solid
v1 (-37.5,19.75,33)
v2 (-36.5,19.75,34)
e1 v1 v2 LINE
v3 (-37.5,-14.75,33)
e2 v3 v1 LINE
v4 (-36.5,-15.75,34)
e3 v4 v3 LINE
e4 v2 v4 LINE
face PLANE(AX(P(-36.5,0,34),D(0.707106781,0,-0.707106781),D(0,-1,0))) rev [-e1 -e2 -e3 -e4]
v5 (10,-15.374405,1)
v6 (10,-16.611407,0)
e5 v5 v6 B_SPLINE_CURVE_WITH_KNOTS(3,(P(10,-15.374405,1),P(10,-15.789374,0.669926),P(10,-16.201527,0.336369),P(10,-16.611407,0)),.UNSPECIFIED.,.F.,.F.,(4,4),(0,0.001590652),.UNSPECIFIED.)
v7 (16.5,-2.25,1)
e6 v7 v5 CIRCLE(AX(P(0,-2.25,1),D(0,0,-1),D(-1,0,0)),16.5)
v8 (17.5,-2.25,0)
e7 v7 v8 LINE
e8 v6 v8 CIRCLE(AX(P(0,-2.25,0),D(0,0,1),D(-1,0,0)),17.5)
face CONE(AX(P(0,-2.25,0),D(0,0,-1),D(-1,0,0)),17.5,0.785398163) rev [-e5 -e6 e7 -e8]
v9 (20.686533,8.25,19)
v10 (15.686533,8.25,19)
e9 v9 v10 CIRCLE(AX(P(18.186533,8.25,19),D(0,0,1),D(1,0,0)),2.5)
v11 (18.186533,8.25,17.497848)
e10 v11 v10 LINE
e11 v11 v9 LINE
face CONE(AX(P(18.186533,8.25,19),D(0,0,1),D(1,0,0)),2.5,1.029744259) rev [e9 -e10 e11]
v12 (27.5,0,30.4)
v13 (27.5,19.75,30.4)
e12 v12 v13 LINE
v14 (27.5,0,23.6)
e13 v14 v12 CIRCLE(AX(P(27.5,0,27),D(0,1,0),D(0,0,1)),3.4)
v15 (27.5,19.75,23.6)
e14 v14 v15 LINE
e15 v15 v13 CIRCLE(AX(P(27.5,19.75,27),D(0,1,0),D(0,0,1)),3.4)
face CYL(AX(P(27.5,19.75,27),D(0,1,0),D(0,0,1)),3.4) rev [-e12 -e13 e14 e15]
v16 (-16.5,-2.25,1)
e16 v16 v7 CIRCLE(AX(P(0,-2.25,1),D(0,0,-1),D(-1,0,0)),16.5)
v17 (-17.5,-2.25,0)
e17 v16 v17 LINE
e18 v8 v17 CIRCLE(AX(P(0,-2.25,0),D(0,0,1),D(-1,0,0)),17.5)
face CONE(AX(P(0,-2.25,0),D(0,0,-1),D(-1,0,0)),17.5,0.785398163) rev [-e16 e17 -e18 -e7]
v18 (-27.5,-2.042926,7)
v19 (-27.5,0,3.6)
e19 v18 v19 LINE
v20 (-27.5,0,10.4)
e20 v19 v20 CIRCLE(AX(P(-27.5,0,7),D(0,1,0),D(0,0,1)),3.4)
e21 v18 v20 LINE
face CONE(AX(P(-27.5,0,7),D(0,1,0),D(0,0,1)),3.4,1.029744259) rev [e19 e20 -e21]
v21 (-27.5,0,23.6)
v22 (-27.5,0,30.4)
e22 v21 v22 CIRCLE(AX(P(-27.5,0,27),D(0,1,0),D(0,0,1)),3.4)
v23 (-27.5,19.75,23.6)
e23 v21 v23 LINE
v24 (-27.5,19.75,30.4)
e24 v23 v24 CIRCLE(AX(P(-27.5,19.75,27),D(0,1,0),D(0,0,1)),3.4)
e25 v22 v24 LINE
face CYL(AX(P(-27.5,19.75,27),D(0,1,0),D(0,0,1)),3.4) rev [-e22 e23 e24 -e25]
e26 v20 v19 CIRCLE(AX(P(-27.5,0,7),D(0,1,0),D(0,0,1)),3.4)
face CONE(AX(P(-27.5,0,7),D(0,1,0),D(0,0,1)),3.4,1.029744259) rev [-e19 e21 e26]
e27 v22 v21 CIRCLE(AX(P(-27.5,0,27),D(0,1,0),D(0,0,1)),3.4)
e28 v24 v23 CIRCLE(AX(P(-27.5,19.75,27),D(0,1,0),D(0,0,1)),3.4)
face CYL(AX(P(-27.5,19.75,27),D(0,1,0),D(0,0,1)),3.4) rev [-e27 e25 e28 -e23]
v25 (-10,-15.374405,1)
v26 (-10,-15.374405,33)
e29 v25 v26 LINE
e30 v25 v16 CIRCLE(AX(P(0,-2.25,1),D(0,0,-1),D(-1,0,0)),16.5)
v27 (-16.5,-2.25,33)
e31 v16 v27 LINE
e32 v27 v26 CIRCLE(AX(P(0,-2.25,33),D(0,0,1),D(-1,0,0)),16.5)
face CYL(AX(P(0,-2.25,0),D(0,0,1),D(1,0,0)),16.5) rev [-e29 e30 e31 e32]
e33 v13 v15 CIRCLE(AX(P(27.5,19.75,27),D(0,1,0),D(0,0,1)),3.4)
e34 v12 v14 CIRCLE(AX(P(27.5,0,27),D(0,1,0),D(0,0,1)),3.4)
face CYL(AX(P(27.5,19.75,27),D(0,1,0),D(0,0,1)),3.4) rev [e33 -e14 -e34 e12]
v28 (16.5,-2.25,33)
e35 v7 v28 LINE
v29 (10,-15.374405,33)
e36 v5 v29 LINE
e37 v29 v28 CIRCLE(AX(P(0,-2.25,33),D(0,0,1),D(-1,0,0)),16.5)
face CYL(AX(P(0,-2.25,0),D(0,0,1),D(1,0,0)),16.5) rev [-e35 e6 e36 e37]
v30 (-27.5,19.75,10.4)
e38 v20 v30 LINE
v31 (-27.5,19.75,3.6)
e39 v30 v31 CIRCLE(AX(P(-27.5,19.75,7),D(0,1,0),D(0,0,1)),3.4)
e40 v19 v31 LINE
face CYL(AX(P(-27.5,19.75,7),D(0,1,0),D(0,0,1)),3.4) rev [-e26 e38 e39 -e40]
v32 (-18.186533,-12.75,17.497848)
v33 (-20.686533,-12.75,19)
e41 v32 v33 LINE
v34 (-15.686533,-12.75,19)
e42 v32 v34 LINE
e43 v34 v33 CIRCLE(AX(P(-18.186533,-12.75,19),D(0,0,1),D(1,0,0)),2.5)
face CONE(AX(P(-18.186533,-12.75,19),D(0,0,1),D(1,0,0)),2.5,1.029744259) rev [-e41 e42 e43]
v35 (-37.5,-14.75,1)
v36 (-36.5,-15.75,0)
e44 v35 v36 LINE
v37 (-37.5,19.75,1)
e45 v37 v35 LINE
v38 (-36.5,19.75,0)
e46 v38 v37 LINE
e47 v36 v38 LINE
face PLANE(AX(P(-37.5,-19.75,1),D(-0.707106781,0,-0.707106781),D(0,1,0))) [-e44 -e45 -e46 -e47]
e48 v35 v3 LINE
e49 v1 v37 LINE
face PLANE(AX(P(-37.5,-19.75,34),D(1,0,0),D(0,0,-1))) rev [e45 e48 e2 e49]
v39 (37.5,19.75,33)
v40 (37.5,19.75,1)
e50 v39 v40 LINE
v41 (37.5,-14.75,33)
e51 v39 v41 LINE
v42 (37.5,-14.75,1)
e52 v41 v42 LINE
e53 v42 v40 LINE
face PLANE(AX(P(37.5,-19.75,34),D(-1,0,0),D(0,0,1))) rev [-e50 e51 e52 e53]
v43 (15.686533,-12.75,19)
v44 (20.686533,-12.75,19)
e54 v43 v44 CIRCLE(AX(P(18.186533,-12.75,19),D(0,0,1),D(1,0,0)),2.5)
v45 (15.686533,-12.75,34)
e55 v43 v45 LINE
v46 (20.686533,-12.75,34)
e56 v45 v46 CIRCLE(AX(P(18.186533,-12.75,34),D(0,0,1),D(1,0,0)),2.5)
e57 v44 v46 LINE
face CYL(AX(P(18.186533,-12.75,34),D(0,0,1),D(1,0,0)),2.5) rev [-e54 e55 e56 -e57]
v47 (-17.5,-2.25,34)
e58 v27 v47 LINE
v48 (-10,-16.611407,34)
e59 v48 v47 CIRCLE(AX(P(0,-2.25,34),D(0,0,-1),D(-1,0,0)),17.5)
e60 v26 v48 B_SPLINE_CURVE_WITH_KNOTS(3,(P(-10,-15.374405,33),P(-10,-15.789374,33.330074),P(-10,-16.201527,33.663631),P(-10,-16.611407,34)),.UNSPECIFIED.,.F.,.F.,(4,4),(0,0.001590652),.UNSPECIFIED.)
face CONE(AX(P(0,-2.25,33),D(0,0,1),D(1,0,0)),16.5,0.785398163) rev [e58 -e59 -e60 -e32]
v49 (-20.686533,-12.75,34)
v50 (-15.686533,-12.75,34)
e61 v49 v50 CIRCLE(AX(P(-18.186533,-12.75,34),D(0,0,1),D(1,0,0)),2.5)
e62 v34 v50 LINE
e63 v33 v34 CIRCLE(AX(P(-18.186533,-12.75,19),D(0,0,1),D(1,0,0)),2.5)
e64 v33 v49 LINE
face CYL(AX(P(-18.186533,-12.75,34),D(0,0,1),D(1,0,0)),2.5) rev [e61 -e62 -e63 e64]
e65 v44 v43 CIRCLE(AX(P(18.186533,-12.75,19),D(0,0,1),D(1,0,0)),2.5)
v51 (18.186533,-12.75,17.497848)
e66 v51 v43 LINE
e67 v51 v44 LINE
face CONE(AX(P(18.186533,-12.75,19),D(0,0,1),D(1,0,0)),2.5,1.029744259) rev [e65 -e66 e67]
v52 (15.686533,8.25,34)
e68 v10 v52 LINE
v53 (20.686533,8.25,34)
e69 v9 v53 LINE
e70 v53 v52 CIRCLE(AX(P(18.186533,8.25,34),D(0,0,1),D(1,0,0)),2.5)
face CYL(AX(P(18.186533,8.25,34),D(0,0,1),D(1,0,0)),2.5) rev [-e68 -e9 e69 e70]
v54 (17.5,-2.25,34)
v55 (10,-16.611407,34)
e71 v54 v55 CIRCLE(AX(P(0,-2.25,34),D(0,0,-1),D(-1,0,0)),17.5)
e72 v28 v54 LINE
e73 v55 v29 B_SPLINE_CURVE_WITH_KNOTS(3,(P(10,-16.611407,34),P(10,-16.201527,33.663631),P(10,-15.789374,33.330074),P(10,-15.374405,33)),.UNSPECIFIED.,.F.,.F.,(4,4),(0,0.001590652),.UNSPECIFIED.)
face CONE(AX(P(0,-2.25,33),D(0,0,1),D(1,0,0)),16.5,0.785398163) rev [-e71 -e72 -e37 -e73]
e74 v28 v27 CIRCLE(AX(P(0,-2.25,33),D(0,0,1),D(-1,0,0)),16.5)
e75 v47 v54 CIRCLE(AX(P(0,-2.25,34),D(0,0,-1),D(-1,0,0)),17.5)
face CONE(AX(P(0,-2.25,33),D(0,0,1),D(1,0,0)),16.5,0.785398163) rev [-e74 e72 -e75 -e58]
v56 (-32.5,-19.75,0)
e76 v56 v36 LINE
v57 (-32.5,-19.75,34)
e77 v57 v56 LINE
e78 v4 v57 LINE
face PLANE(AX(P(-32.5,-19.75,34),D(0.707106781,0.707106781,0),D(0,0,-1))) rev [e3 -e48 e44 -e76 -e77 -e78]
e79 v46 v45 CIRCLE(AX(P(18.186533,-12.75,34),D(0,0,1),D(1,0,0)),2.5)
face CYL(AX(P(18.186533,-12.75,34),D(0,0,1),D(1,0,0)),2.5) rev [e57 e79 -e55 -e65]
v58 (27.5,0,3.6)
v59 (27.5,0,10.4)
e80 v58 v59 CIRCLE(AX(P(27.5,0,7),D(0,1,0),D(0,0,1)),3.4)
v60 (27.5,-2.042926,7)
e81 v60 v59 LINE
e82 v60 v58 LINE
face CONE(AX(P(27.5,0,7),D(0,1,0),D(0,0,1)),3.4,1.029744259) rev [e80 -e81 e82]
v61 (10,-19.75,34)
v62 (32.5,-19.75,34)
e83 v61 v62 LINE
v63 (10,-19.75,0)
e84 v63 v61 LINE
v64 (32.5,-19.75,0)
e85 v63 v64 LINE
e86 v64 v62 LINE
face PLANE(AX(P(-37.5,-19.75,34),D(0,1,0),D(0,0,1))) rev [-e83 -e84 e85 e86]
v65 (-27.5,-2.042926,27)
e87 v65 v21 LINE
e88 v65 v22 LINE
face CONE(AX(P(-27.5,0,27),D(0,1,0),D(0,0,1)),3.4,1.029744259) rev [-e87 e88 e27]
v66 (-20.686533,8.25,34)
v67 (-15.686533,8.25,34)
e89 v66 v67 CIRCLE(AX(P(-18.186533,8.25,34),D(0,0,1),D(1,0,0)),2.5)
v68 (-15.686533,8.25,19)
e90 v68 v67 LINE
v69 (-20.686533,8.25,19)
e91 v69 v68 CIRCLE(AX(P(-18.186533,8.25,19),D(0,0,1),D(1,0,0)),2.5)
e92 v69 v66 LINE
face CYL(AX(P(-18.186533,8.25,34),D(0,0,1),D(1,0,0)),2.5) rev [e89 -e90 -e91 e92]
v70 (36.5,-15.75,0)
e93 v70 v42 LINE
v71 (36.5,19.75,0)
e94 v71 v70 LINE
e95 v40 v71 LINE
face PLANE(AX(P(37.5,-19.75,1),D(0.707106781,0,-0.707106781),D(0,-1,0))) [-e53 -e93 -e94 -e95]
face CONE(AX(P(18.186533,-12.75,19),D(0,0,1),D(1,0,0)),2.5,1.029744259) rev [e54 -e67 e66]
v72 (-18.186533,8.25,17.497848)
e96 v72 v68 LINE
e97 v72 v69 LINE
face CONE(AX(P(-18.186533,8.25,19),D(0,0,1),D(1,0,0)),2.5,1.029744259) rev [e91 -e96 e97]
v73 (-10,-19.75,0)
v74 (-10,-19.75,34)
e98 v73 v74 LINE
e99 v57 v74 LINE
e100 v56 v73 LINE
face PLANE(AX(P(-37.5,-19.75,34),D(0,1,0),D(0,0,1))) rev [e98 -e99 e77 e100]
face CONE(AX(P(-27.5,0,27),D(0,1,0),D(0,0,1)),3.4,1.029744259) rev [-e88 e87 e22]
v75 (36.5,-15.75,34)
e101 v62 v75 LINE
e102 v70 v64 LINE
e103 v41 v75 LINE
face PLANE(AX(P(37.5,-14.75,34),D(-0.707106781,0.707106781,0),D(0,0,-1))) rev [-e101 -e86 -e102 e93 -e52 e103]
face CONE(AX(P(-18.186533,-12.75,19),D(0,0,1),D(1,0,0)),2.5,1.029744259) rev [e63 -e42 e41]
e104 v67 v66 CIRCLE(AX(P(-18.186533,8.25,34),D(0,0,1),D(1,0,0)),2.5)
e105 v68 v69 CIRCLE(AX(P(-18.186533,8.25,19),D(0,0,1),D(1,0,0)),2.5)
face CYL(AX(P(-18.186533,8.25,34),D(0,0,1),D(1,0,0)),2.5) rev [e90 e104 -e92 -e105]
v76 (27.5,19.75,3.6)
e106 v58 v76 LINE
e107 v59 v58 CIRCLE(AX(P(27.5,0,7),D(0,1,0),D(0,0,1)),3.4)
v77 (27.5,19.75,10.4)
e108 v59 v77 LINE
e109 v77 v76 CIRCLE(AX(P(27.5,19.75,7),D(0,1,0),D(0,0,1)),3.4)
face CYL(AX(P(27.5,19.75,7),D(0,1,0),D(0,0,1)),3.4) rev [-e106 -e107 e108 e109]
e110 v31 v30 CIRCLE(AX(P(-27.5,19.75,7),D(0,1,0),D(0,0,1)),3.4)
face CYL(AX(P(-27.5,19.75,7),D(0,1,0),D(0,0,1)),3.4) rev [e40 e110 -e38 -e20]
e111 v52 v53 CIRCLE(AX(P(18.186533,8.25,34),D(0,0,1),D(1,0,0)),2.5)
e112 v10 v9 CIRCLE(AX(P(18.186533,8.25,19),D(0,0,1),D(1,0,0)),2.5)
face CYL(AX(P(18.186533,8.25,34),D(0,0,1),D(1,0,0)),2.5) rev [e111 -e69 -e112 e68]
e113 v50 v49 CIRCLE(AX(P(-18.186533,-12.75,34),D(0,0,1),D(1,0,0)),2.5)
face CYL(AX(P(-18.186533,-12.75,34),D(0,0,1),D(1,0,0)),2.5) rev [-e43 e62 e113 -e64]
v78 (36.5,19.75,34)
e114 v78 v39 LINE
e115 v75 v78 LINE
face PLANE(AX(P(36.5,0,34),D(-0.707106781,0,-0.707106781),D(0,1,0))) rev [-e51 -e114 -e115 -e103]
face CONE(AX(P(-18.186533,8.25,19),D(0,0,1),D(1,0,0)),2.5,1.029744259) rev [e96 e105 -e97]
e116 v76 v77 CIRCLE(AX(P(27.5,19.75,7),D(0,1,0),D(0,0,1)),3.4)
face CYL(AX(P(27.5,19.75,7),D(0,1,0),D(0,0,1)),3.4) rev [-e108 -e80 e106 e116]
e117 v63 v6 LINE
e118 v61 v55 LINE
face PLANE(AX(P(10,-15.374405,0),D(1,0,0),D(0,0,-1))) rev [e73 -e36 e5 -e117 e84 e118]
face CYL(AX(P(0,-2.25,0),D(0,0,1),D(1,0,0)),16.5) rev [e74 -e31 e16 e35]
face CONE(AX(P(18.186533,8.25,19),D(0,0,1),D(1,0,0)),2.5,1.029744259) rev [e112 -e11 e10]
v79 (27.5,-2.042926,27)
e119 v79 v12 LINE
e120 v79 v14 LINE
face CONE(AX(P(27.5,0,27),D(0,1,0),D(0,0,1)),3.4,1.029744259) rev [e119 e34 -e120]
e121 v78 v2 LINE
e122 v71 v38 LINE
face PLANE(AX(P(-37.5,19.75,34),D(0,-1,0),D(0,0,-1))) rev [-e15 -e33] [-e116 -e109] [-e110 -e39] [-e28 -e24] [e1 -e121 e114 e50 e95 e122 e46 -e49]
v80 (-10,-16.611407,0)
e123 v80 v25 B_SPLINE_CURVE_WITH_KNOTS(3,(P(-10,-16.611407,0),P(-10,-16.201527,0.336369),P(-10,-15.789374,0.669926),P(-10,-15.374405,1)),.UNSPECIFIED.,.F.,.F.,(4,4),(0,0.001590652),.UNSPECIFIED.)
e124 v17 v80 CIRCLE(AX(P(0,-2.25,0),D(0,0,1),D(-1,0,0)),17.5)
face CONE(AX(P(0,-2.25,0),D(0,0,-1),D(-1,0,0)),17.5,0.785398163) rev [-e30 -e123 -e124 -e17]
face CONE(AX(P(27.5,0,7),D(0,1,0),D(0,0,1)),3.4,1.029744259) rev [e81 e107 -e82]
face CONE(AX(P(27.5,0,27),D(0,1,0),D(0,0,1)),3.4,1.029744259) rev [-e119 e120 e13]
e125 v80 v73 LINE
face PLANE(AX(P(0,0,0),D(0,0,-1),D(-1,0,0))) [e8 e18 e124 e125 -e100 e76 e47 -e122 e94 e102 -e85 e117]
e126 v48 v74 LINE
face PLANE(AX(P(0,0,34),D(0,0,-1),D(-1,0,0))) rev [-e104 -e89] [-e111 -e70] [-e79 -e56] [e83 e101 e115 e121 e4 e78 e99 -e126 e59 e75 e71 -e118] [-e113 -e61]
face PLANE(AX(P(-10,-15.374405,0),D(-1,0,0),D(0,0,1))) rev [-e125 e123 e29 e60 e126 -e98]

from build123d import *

# Parameters (mm, degrees)
SKETCH_1_W             = 75
SKETCH_1_H             = 39.5
EXTRUDE_1_DEPTH        = 34
SKETCH_2_R             = 16.5
CUT_EXTRUDE_1_DEPTH    = 55.335186574
SKETCH_3_W             = 20
SKETCH_3_H             = 4.375595252
CUT_EXTRUDE_2_DEPTH    = 55.335186574
HOLE_WIZARD_M8_1_D     = 6.8
HOLE_WIZARD_M8_1_DEPTH = 19.75
HOLE_WIZARD_M8_1_TIP   = 2.042926105
CHAMFER_1_SIZE         = 5
CHAMFER_2_SIZE         = 1
HOLE_WIZARD_M6_1_D     = 5
HOLE_WIZARD_M6_1_DEPTH = 15
HOLE_WIZARD_M6_1_TIP   = 1.502151548


with BuildPart() as part:
    # 草图1 → 凸台-拉伸1 (new body)
    with BuildSketch(Plane.XY):
        Rectangle(SKETCH_1_W, SKETCH_1_H)
    extrude(amount=EXTRUDE_1_DEPTH)

    # 草图2 → 切除-拉伸1 (cut, through all)
    with BuildSketch(Plane.XY.offset(34)):
        with Locations((0, -2.25)):
            Circle(SKETCH_2_R)
    extrude(amount=-CUT_EXTRUDE_1_DEPTH, mode=Mode.SUBTRACT)

    # 草图3 → 切除-拉伸2 (cut, through all)
    with BuildSketch(Plane.XY.offset(34)):
        with Locations((0, -17.562202374)):
            Rectangle(SKETCH_3_W, SKETCH_3_H)
    extrude(amount=-CUT_EXTRUDE_2_DEPTH, mode=Mode.SUBTRACT)

    # M8 螺纹孔1
    with Locations(Plane(origin=(0, 19.75, 0), x_dir=(1, 0, 0), z_dir=(0, 1, 0))):
        with Locations((-27.5, -7), (-27.5, -27), (27.5, -27), (27.5, -7)):
            Hole(HOLE_WIZARD_M8_1_D / 2, depth=HOLE_WIZARD_M8_1_DEPTH)
            with Locations((0, 0, -(HOLE_WIZARD_M8_1_DEPTH + HOLE_WIZARD_M8_1_TIP / 2))):  # 118° drill point
                Cone(0, HOLE_WIZARD_M8_1_D / 2, HOLE_WIZARD_M8_1_TIP, mode=Mode.SUBTRACT)

    # 倒角1
    chamfer_1_edges = [part.edges().sort_by_distance(p)[0] for p in [
        (37.5, -19.75, 17),
        (-37.5, -19.75, 17),
    ]]
    chamfer(chamfer_1_edges, length=CHAMFER_1_SIZE)

    # 倒角2
    chamfer_2_edges = [part.edges().sort_by_distance(p)[0] for p in [
        (-37.5, 2.5, 34),
        (0, 14.25, 0),
        (0, 14.25, 34),
        (-37.5, 2.5, 0),
        (37.5, 2.5, 0),
        (37.5, 2.5, 34),
    ]]
    chamfer(chamfer_2_edges, length=CHAMFER_2_SIZE)

    # M6 螺纹孔1
    with Locations(Plane.XY.offset(34)):
        with Locations((-18.186533479, 8.25), (-18.186533479, -12.75), (18.186533479, 8.25), (18.186533479, -12.75)):
            Hole(HOLE_WIZARD_M6_1_D / 2, depth=HOLE_WIZARD_M6_1_DEPTH)
            with Locations((0, 0, -(HOLE_WIZARD_M6_1_DEPTH + HOLE_WIZARD_M6_1_TIP / 2))):  # 118° drill point
                Cone(0, HOLE_WIZARD_M6_1_D / 2, HOLE_WIZARD_M6_1_TIP, mode=Mode.SUBTRACT)


solid = part.part
